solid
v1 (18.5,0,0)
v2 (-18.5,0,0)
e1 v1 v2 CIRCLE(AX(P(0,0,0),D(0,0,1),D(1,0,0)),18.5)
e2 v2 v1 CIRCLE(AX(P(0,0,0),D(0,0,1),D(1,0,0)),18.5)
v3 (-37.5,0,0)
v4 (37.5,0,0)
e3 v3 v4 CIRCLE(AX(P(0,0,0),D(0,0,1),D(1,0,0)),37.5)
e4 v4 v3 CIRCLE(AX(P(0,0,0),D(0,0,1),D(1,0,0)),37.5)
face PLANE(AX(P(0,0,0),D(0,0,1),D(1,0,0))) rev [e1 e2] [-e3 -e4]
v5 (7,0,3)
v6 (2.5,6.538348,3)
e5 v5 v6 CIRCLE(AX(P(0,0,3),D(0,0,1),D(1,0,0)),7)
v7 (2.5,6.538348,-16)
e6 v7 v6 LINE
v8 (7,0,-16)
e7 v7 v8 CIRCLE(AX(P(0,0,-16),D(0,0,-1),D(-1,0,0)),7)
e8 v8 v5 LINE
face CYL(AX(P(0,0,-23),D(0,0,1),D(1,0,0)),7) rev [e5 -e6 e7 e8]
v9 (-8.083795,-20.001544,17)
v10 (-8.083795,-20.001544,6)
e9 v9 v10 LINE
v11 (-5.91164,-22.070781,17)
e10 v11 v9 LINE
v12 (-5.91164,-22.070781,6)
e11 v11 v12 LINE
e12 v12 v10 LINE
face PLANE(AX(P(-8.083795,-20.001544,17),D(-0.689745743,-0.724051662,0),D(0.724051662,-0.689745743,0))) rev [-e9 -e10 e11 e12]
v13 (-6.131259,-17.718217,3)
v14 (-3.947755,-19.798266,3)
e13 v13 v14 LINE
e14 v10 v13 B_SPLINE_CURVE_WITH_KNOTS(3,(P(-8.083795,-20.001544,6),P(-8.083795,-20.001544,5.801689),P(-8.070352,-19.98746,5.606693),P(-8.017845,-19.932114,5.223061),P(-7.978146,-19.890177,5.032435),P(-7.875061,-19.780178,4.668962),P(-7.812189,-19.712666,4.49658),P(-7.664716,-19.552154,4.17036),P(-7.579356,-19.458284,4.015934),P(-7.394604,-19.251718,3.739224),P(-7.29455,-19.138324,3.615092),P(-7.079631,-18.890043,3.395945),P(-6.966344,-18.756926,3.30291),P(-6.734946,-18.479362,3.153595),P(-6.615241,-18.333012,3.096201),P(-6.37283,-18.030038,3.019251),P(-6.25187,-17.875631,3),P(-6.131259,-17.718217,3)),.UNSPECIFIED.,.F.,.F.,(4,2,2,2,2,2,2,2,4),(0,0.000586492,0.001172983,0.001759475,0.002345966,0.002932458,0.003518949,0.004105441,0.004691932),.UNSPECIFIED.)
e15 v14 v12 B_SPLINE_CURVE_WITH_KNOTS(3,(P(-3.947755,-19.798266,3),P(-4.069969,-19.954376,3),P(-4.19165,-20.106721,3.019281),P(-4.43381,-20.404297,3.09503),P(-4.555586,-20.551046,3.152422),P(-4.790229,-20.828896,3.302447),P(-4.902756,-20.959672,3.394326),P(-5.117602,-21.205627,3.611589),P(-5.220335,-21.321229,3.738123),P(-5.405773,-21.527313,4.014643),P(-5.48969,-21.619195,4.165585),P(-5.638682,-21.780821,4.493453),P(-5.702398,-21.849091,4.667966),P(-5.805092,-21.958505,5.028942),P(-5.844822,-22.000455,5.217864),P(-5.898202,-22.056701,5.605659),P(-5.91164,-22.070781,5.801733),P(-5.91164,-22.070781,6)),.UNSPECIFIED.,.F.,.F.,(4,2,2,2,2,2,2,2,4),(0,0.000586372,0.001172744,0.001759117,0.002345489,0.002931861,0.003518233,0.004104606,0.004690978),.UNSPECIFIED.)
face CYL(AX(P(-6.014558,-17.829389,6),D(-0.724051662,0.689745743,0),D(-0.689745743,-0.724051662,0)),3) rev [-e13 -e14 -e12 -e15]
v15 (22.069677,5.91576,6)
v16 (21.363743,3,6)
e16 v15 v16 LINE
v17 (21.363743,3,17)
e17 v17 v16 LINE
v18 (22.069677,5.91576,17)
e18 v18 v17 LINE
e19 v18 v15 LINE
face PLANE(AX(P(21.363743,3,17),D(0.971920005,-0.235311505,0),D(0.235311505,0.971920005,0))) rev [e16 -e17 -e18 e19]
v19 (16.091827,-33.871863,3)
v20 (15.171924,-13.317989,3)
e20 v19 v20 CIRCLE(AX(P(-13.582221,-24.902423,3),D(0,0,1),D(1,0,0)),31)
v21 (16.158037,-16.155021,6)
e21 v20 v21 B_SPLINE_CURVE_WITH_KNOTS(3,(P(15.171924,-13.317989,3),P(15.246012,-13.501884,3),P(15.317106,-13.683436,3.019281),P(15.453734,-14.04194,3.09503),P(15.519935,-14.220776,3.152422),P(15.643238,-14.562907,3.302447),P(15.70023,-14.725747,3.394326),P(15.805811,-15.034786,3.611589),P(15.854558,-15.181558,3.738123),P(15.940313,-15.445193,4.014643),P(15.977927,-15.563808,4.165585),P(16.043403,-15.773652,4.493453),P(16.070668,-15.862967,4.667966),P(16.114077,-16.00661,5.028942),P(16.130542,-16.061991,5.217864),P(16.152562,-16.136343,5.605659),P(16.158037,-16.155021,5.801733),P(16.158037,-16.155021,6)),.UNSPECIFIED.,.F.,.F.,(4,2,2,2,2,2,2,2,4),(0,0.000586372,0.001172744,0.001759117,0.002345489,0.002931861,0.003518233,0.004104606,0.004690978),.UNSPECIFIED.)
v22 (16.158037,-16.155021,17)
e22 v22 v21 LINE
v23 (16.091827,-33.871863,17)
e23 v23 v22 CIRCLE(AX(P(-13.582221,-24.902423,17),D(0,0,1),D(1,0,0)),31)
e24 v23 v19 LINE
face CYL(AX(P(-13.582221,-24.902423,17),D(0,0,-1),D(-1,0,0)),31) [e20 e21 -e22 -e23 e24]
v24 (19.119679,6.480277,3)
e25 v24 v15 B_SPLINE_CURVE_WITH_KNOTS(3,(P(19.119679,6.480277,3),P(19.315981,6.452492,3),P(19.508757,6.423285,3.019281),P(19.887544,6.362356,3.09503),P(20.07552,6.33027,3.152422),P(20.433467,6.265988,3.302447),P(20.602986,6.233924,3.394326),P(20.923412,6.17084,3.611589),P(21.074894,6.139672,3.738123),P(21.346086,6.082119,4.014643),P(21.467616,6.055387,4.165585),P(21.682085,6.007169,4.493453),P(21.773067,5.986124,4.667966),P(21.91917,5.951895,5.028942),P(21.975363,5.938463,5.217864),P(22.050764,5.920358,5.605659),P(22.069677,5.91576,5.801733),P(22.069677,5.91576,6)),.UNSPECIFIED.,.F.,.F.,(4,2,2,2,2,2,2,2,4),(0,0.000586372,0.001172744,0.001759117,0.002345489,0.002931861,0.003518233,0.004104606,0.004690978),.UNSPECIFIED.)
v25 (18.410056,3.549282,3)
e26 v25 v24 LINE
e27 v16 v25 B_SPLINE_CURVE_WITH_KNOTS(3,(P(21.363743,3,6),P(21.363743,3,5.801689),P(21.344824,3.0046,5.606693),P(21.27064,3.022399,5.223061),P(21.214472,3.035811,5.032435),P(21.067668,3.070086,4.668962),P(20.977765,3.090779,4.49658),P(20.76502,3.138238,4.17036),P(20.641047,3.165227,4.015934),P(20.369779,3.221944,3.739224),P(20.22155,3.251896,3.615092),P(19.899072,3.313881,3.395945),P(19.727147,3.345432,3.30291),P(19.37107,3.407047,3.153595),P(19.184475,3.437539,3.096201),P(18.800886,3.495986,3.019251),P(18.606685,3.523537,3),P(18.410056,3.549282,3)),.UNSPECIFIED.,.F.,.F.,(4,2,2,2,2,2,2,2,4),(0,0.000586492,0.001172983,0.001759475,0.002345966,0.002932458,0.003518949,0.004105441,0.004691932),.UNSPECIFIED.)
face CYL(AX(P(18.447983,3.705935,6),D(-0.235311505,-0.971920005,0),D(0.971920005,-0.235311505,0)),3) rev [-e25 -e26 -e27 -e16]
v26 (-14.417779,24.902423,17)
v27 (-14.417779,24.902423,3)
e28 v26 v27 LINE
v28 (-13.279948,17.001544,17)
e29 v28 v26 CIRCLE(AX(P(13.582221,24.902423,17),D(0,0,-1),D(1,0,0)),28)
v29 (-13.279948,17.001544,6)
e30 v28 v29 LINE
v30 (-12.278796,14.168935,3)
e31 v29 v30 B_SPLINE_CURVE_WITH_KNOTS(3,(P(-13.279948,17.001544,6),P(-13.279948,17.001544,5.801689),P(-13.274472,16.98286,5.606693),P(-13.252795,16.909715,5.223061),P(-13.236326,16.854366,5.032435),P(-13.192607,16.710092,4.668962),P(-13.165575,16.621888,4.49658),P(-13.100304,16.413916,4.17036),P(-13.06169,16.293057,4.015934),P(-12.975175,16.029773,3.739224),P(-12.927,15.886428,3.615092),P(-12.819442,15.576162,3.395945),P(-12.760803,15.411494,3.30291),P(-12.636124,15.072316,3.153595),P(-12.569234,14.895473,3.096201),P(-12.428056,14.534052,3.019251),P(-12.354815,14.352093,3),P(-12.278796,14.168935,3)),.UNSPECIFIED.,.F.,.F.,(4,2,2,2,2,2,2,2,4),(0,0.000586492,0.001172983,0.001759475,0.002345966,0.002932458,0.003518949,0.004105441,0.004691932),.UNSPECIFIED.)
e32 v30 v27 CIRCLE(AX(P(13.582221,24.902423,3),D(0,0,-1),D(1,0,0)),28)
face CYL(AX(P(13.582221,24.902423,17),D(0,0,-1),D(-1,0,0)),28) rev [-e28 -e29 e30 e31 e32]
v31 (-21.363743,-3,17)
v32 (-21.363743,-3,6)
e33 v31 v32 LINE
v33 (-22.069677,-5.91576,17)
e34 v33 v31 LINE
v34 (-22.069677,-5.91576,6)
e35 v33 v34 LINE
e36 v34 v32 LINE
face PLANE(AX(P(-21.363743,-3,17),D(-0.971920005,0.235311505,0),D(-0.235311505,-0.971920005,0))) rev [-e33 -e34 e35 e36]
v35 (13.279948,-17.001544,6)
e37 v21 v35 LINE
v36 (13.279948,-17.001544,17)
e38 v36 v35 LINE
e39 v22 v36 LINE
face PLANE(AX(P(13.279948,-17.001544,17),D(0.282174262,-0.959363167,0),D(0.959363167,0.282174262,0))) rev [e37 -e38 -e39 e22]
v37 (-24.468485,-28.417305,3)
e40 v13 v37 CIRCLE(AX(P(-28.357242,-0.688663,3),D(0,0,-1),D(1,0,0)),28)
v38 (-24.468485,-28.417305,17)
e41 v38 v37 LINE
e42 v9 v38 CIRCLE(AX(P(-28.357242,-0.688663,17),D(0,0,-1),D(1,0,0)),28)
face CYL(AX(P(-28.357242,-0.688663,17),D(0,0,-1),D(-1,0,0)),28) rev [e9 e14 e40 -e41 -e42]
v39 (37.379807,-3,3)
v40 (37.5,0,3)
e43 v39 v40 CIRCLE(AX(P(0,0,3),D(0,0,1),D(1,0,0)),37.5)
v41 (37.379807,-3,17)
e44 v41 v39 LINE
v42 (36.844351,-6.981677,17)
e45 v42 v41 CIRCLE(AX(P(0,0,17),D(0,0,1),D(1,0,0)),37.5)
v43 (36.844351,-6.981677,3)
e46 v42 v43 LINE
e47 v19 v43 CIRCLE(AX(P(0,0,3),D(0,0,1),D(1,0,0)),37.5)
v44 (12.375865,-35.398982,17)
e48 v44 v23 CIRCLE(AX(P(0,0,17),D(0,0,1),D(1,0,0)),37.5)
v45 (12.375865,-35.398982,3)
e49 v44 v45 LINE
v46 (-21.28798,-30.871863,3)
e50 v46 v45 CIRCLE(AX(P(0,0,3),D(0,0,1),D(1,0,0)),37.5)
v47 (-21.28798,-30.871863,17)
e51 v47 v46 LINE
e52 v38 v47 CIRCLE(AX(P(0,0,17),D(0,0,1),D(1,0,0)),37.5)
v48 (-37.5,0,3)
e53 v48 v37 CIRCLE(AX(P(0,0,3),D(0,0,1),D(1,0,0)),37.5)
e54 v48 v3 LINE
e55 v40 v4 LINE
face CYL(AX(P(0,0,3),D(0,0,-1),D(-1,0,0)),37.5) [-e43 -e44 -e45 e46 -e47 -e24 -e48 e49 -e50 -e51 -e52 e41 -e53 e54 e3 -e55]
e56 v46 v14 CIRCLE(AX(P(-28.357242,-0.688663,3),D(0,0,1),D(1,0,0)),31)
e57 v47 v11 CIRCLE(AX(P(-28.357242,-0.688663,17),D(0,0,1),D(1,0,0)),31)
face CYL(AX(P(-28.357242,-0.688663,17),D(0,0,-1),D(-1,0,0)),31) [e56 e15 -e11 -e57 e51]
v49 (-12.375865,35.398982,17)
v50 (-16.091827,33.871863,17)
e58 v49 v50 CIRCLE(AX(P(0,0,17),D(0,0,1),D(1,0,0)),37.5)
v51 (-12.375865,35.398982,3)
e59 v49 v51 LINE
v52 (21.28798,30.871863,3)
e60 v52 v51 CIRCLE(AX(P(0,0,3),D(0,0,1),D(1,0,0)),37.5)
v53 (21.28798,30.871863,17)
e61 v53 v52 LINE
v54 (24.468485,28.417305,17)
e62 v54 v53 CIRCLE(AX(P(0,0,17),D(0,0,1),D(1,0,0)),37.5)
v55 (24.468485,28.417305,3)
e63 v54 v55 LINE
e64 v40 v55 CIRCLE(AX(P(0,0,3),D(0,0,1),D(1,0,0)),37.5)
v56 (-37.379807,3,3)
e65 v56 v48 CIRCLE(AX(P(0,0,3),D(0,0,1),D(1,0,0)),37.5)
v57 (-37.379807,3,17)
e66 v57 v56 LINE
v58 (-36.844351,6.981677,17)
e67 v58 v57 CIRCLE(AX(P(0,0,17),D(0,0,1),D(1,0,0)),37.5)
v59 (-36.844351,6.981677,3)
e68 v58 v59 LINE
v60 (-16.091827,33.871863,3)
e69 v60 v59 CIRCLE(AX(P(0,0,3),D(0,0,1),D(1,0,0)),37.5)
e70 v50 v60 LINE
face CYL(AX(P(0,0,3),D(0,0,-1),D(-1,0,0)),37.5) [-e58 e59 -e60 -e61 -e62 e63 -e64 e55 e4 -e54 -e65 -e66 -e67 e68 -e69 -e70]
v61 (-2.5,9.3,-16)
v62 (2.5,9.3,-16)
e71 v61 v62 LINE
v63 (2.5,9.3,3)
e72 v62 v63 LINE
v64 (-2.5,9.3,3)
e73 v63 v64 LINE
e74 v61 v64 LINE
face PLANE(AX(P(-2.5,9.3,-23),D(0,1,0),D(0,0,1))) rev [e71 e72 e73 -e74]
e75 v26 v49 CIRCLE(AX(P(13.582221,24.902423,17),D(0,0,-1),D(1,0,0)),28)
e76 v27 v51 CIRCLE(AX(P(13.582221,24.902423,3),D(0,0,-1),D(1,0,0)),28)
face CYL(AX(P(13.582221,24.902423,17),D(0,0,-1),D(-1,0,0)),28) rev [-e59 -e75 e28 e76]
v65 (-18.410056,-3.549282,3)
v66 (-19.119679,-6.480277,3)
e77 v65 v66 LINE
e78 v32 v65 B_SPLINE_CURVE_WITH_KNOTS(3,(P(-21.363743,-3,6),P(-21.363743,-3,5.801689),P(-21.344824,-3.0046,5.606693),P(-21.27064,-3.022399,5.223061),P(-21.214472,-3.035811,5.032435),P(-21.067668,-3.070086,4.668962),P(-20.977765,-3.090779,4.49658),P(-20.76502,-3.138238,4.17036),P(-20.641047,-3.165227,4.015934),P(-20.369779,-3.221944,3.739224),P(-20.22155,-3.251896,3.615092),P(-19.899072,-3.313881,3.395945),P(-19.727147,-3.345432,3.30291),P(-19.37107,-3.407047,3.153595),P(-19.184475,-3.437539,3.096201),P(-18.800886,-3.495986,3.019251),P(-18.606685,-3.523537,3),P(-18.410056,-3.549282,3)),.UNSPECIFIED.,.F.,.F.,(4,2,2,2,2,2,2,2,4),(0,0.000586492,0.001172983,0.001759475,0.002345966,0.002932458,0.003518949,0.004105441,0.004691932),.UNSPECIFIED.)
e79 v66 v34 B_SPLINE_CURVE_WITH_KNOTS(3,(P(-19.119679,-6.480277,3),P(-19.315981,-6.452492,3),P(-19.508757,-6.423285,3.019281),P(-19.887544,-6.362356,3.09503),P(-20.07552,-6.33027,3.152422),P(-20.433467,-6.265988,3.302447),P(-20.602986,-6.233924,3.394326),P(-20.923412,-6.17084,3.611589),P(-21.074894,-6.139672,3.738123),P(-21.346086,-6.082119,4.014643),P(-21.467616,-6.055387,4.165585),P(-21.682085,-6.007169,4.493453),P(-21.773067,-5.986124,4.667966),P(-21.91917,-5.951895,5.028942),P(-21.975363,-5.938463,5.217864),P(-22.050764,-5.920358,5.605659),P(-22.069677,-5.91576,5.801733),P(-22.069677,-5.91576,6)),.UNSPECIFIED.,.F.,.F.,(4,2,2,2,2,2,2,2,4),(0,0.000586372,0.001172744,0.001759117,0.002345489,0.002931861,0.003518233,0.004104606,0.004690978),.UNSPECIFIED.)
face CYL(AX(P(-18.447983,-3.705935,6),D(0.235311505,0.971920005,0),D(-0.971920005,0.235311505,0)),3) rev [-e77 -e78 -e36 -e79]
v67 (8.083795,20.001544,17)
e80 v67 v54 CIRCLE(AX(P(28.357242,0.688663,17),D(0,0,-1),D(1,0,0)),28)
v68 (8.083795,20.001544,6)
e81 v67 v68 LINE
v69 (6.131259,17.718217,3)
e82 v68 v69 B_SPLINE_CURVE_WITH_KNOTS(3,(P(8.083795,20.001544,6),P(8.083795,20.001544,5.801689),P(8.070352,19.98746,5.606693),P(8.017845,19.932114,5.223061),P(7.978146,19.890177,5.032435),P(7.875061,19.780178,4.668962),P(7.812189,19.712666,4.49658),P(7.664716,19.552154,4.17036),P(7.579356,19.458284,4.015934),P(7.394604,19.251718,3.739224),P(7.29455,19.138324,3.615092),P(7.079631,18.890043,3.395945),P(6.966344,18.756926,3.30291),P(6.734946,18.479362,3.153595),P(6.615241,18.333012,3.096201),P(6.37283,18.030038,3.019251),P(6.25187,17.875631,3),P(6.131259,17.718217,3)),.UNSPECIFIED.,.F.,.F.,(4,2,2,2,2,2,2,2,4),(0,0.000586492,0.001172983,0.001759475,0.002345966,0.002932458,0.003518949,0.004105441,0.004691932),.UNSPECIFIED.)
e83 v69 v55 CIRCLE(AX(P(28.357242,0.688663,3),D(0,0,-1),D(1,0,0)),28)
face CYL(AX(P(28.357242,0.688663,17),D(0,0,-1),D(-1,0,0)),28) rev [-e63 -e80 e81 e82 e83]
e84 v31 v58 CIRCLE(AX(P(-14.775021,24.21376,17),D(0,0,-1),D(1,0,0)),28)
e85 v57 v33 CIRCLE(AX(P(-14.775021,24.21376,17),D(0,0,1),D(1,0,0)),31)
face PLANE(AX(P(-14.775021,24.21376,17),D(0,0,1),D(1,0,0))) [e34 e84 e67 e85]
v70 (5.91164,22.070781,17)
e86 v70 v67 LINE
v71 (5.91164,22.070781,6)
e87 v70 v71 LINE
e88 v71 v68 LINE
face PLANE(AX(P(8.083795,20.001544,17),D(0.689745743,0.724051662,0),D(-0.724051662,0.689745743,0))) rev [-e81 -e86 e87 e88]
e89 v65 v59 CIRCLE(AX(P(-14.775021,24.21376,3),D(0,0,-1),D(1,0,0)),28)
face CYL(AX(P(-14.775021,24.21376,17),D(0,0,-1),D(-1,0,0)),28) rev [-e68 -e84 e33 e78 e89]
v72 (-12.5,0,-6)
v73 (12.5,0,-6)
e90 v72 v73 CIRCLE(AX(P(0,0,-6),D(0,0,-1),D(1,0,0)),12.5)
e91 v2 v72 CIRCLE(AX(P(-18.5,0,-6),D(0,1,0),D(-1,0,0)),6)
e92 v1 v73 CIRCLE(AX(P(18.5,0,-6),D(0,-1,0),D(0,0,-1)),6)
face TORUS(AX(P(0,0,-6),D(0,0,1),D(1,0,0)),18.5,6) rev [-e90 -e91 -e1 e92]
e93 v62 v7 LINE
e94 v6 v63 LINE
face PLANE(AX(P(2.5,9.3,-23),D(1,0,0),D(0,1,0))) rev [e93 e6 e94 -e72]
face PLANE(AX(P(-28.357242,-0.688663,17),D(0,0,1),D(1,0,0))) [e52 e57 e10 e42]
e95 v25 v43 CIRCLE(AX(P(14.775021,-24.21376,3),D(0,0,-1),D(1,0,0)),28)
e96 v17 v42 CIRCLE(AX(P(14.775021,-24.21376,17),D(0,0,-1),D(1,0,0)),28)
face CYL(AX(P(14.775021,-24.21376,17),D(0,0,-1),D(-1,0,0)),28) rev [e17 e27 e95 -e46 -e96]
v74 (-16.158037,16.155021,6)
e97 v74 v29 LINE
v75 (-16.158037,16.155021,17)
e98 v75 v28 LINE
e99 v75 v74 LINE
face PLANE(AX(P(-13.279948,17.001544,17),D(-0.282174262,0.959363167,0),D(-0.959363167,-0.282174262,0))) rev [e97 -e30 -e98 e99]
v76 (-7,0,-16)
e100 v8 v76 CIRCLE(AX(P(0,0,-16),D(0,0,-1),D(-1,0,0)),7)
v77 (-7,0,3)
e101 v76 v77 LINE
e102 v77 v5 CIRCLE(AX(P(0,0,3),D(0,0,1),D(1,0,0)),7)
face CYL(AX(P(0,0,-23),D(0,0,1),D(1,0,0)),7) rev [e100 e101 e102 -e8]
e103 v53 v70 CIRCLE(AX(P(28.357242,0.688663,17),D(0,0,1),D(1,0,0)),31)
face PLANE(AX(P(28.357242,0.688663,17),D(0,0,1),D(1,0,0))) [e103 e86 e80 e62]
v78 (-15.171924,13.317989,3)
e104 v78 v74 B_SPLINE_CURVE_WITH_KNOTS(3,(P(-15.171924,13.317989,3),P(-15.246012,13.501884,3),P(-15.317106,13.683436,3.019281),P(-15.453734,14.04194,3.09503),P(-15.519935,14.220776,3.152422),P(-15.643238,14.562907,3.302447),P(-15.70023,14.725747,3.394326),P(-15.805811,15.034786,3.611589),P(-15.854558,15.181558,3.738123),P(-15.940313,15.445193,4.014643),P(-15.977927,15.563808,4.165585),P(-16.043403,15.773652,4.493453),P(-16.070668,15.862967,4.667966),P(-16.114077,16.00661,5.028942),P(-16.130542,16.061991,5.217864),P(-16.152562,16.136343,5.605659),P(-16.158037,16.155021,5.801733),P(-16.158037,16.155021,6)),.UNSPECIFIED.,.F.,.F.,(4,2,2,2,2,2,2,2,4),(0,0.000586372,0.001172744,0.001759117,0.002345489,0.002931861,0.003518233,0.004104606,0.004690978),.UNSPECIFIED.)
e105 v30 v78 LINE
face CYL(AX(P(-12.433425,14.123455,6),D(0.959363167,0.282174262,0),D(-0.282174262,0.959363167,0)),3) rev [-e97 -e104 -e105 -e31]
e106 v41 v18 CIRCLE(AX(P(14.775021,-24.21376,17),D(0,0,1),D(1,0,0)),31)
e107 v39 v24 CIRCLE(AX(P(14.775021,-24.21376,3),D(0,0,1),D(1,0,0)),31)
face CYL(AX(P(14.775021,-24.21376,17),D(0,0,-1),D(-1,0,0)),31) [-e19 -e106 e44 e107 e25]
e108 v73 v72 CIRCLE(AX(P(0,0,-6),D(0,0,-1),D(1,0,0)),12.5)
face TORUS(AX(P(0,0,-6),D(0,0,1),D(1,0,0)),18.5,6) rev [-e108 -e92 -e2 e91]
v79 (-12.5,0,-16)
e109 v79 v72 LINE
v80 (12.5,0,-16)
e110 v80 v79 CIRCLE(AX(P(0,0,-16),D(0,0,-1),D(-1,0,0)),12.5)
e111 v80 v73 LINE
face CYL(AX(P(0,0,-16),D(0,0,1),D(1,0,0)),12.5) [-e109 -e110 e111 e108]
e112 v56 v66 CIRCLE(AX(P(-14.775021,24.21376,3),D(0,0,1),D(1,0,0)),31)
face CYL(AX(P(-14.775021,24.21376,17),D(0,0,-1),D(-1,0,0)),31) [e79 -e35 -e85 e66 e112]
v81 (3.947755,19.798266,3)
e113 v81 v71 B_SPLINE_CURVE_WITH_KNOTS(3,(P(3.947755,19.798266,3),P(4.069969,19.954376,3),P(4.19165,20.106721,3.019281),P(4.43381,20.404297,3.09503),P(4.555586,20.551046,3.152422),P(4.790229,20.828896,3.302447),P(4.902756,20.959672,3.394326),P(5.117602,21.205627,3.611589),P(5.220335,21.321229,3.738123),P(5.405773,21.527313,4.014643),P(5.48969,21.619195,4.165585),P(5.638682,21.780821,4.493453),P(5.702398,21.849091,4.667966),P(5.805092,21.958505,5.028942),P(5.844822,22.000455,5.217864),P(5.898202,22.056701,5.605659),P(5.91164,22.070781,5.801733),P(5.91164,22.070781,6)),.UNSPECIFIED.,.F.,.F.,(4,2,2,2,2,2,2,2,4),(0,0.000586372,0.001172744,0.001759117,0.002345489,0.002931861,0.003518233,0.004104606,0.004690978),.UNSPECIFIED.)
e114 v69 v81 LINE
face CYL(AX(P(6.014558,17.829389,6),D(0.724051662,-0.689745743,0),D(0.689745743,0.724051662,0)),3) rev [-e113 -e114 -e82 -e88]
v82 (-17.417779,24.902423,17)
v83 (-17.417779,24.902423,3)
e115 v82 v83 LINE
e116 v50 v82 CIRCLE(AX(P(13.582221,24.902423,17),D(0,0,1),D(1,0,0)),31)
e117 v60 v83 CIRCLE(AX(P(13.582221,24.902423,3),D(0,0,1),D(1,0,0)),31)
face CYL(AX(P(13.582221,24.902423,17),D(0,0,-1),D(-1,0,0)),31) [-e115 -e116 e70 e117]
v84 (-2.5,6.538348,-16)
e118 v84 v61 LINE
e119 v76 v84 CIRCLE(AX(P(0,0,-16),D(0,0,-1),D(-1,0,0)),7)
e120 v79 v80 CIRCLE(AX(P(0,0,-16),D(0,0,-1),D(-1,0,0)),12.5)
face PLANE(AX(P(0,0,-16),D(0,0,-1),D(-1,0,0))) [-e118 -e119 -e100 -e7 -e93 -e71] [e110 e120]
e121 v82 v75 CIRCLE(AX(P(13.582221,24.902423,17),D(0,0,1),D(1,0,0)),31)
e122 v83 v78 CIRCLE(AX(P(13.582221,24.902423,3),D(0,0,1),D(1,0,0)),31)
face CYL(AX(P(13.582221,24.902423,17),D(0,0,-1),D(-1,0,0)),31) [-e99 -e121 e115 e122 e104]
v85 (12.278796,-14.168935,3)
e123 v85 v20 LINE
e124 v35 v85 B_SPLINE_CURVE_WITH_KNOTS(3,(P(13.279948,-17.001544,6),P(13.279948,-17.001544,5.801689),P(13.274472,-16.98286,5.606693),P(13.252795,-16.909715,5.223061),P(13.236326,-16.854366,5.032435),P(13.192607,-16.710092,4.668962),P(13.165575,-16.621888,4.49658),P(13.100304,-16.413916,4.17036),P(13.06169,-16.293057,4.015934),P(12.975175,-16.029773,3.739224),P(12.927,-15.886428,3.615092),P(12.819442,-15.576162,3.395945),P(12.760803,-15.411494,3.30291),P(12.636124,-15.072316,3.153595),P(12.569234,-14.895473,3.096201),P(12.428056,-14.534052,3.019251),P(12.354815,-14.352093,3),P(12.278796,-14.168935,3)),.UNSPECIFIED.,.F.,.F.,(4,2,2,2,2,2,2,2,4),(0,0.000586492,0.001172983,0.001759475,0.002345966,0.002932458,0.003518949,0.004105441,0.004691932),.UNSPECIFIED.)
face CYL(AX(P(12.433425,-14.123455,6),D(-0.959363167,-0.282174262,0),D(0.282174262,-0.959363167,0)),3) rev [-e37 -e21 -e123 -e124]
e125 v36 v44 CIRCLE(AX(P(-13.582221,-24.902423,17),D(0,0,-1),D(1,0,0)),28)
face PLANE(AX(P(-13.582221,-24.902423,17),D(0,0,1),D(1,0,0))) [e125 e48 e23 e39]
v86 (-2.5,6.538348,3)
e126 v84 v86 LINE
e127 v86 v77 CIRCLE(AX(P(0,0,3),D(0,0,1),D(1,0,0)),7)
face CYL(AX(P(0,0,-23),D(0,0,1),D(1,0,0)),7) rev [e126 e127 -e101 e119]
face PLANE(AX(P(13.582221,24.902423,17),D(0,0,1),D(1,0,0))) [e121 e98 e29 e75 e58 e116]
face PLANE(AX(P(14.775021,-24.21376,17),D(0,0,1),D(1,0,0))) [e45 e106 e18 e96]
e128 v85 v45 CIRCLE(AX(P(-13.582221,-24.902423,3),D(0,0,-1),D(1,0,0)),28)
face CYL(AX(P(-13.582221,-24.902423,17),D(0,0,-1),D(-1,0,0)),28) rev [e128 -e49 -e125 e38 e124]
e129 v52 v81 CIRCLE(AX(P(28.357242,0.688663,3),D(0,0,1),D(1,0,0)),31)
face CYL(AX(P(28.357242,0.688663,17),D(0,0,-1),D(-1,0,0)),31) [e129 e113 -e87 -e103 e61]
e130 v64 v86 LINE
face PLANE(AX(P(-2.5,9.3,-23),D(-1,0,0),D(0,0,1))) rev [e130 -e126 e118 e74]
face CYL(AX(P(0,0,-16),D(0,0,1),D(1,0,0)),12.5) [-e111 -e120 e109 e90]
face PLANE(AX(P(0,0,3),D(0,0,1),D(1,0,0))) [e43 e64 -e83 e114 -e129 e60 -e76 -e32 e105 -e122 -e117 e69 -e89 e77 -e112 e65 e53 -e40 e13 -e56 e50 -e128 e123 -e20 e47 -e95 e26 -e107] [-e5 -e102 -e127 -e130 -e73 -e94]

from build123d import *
from build123d.topology import SkipClean

# Parameters (mm, degrees)
BACK_DISC_SKETCH_75_R  = 37.5
BACK_DISC_75X3_DEPTH   = 3
VANES_6X_DEPTH         = 14
VANE_ROOT_FILLETS_R3_R = 3
HUB_SKETCH_25_R        = 12.5
HUB_25X16_DEPTH        = 16
HUB_FILLET_R6_R        = 6
KEYED_BORE_14_DEPTH    = 26


with BuildPart() as part:
    # Back Disc Sketch Ø75 → Back Disc Ø75x3 (new body)
    with BuildSketch(Plane.XY):
        Circle(BACK_DISC_SKETCH_75_R)
    extrude(amount=BACK_DISC_75X3_DEPTH)

    # Vane Profiles 6x Sketch → Vanes 6x (add)
    with SkipClean():  # the faces are left unmerged after this step: merging them gives an invalid solid
        with BuildSketch(Plane.XY.offset(3)):
            with BuildLine():
                Line((-21.363742831, -3), (-22.069677344, -5.915760015))
                ThreePointArc((-22.069677344, -5.915760015), (-30.375240954, -2.574915234), (-37.379807383, 3))
                ThreePointArc((-37.379807383, 3), (-37.165438921, 4.998014583), (-36.844350715, 6.981677477))
                ThreePointArc((-36.844350715, 6.981677477), (-29.948334758, 0.681430448), (-21.363742831, -3))
            make_face()
            with BuildLine():
                Line((-13.279947627, 17.001544011), (-16.158037127, 16.155021226))
                ThreePointArc((-16.158037127, 16.155021226), (-17.417562483, 25.018272695), (-16.09182748, 33.871862782))
                ThreePointArc((-16.09182748, 33.871862782), (-14.254311863, 34.68522154), (-12.375865302, 35.398982443))
                ThreePointArc((-12.375865302, 35.398982443), (-14.384031301, 26.276733925), (-13.279947627, 17.001544011))
            make_face()
            with BuildLine():
                Line((8.083795204, 20.001544011), (5.911640217, 22.070781241))
                ThreePointArc((5.911640217, 22.070781241), (12.957678472, 27.59318793), (21.287979903, 30.871862782))
                ThreePointArc((21.287979903, 30.871862782), (22.911127058, 29.687206957), (24.468485413, 28.417304967))
                ThreePointArc((24.468485413, 28.417304967), (15.564303458, 25.595303478), (8.083795204, 20.001544011))
            make_face()
            with BuildLine():
                Line((21.363742831, 3), (22.069677344, 5.915760015))
                ThreePointArc((22.069677344, 5.915760015), (30.375240954, 2.574915234), (37.379807383, -3))
                ThreePointArc((37.379807383, -3), (37.165438921, -4.998014583), (36.844350715, -6.981677477))
                ThreePointArc((36.844350715, -6.981677477), (29.948334758, -0.681430448), (21.363742831, 3))
            make_face()
            with BuildLine():
                Line((13.279947627, -17.001544011), (16.158037127, -16.155021226))
                ThreePointArc((16.158037127, -16.155021226), (17.417562483, -25.018272695), (16.09182748, -33.871862782))
                ThreePointArc((16.09182748, -33.871862782), (14.254311863, -34.68522154), (12.375865302, -35.398982443))
                ThreePointArc((12.375865302, -35.398982443), (14.384031301, -26.276733925), (13.279947627, -17.001544011))
            make_face()
            with BuildLine():
                Line((-8.083795204, -20.001544011), (-5.911640217, -22.070781241))
                ThreePointArc((-5.911640217, -22.070781241), (-12.957678472, -27.59318793), (-21.287979903, -30.871862782))
                ThreePointArc((-21.287979903, -30.871862782), (-22.911127058, -29.687206957), (-24.468485413, -28.417304967))
                ThreePointArc((-24.468485413, -28.417304967), (-15.564303458, -25.595303478), (-8.083795204, -20.001544011))
            make_face()
        extrude(amount=VANES_6X_DEPTH)

    # Vane Root Fillets R3
    vane_root_fillets_r3_edges = [part.edges().sort_by_distance(p)[0] for p in [
        (-14.718992377, 16.578282619, 3),
        (6.99771771, 21.036162626, 3),
        (21.716710087, 4.457880007, 3),
        (14.718992377, -16.578282619, 3),
        (-6.99771771, -21.036162626, 3),
        (-21.716710087, -4.457880007, 3),
    ]]
    fillet(vane_root_fillets_r3_edges, radius=VANE_ROOT_FILLETS_R3_R)

    # Hub Sketch Ø25 → Hub Ø25x16 (add)
    with SkipClean():  # the faces are left unmerged after this step: merging them gives an invalid solid
        with BuildSketch(Plane(origin=(0, 0, 0), x_dir=(-1, 0, 0), z_dir=(0, 0, -1))):
            Circle(HUB_SKETCH_25_R)
        extrude(amount=HUB_25X16_DEPTH)

    # Hub Fillet R6
    hub_fillet_r6_edges = [part.edges().sort_by_distance(p)[0] for p in [
        (12.5, 0, 0),
    ]]
    fillet(hub_fillet_r6_edges, radius=HUB_FILLET_R6_R)

    # Keyed Bore Sketch Ø14 → Keyed Bore Ø14 (cut)
    with SkipClean():  # the faces are left unmerged after this step: merging them gives an invalid solid
        with BuildSketch(Plane.XY.offset(3)):
            with BuildLine():
                Line((-2.5, 9.3), (2.5, 9.3))
                Line((2.5, 9.3), (2.5, 6.538348415))
                ThreePointArc((2.5, 6.538348415), (0, -7), (-2.5, 6.538348415))
                Line((-2.5, 6.538348415), (-2.5, 9.3))
            make_face()
        extrude(amount=-KEYED_BORE_14_DEPTH, mode=Mode.SUBTRACT)


solid = part.part
